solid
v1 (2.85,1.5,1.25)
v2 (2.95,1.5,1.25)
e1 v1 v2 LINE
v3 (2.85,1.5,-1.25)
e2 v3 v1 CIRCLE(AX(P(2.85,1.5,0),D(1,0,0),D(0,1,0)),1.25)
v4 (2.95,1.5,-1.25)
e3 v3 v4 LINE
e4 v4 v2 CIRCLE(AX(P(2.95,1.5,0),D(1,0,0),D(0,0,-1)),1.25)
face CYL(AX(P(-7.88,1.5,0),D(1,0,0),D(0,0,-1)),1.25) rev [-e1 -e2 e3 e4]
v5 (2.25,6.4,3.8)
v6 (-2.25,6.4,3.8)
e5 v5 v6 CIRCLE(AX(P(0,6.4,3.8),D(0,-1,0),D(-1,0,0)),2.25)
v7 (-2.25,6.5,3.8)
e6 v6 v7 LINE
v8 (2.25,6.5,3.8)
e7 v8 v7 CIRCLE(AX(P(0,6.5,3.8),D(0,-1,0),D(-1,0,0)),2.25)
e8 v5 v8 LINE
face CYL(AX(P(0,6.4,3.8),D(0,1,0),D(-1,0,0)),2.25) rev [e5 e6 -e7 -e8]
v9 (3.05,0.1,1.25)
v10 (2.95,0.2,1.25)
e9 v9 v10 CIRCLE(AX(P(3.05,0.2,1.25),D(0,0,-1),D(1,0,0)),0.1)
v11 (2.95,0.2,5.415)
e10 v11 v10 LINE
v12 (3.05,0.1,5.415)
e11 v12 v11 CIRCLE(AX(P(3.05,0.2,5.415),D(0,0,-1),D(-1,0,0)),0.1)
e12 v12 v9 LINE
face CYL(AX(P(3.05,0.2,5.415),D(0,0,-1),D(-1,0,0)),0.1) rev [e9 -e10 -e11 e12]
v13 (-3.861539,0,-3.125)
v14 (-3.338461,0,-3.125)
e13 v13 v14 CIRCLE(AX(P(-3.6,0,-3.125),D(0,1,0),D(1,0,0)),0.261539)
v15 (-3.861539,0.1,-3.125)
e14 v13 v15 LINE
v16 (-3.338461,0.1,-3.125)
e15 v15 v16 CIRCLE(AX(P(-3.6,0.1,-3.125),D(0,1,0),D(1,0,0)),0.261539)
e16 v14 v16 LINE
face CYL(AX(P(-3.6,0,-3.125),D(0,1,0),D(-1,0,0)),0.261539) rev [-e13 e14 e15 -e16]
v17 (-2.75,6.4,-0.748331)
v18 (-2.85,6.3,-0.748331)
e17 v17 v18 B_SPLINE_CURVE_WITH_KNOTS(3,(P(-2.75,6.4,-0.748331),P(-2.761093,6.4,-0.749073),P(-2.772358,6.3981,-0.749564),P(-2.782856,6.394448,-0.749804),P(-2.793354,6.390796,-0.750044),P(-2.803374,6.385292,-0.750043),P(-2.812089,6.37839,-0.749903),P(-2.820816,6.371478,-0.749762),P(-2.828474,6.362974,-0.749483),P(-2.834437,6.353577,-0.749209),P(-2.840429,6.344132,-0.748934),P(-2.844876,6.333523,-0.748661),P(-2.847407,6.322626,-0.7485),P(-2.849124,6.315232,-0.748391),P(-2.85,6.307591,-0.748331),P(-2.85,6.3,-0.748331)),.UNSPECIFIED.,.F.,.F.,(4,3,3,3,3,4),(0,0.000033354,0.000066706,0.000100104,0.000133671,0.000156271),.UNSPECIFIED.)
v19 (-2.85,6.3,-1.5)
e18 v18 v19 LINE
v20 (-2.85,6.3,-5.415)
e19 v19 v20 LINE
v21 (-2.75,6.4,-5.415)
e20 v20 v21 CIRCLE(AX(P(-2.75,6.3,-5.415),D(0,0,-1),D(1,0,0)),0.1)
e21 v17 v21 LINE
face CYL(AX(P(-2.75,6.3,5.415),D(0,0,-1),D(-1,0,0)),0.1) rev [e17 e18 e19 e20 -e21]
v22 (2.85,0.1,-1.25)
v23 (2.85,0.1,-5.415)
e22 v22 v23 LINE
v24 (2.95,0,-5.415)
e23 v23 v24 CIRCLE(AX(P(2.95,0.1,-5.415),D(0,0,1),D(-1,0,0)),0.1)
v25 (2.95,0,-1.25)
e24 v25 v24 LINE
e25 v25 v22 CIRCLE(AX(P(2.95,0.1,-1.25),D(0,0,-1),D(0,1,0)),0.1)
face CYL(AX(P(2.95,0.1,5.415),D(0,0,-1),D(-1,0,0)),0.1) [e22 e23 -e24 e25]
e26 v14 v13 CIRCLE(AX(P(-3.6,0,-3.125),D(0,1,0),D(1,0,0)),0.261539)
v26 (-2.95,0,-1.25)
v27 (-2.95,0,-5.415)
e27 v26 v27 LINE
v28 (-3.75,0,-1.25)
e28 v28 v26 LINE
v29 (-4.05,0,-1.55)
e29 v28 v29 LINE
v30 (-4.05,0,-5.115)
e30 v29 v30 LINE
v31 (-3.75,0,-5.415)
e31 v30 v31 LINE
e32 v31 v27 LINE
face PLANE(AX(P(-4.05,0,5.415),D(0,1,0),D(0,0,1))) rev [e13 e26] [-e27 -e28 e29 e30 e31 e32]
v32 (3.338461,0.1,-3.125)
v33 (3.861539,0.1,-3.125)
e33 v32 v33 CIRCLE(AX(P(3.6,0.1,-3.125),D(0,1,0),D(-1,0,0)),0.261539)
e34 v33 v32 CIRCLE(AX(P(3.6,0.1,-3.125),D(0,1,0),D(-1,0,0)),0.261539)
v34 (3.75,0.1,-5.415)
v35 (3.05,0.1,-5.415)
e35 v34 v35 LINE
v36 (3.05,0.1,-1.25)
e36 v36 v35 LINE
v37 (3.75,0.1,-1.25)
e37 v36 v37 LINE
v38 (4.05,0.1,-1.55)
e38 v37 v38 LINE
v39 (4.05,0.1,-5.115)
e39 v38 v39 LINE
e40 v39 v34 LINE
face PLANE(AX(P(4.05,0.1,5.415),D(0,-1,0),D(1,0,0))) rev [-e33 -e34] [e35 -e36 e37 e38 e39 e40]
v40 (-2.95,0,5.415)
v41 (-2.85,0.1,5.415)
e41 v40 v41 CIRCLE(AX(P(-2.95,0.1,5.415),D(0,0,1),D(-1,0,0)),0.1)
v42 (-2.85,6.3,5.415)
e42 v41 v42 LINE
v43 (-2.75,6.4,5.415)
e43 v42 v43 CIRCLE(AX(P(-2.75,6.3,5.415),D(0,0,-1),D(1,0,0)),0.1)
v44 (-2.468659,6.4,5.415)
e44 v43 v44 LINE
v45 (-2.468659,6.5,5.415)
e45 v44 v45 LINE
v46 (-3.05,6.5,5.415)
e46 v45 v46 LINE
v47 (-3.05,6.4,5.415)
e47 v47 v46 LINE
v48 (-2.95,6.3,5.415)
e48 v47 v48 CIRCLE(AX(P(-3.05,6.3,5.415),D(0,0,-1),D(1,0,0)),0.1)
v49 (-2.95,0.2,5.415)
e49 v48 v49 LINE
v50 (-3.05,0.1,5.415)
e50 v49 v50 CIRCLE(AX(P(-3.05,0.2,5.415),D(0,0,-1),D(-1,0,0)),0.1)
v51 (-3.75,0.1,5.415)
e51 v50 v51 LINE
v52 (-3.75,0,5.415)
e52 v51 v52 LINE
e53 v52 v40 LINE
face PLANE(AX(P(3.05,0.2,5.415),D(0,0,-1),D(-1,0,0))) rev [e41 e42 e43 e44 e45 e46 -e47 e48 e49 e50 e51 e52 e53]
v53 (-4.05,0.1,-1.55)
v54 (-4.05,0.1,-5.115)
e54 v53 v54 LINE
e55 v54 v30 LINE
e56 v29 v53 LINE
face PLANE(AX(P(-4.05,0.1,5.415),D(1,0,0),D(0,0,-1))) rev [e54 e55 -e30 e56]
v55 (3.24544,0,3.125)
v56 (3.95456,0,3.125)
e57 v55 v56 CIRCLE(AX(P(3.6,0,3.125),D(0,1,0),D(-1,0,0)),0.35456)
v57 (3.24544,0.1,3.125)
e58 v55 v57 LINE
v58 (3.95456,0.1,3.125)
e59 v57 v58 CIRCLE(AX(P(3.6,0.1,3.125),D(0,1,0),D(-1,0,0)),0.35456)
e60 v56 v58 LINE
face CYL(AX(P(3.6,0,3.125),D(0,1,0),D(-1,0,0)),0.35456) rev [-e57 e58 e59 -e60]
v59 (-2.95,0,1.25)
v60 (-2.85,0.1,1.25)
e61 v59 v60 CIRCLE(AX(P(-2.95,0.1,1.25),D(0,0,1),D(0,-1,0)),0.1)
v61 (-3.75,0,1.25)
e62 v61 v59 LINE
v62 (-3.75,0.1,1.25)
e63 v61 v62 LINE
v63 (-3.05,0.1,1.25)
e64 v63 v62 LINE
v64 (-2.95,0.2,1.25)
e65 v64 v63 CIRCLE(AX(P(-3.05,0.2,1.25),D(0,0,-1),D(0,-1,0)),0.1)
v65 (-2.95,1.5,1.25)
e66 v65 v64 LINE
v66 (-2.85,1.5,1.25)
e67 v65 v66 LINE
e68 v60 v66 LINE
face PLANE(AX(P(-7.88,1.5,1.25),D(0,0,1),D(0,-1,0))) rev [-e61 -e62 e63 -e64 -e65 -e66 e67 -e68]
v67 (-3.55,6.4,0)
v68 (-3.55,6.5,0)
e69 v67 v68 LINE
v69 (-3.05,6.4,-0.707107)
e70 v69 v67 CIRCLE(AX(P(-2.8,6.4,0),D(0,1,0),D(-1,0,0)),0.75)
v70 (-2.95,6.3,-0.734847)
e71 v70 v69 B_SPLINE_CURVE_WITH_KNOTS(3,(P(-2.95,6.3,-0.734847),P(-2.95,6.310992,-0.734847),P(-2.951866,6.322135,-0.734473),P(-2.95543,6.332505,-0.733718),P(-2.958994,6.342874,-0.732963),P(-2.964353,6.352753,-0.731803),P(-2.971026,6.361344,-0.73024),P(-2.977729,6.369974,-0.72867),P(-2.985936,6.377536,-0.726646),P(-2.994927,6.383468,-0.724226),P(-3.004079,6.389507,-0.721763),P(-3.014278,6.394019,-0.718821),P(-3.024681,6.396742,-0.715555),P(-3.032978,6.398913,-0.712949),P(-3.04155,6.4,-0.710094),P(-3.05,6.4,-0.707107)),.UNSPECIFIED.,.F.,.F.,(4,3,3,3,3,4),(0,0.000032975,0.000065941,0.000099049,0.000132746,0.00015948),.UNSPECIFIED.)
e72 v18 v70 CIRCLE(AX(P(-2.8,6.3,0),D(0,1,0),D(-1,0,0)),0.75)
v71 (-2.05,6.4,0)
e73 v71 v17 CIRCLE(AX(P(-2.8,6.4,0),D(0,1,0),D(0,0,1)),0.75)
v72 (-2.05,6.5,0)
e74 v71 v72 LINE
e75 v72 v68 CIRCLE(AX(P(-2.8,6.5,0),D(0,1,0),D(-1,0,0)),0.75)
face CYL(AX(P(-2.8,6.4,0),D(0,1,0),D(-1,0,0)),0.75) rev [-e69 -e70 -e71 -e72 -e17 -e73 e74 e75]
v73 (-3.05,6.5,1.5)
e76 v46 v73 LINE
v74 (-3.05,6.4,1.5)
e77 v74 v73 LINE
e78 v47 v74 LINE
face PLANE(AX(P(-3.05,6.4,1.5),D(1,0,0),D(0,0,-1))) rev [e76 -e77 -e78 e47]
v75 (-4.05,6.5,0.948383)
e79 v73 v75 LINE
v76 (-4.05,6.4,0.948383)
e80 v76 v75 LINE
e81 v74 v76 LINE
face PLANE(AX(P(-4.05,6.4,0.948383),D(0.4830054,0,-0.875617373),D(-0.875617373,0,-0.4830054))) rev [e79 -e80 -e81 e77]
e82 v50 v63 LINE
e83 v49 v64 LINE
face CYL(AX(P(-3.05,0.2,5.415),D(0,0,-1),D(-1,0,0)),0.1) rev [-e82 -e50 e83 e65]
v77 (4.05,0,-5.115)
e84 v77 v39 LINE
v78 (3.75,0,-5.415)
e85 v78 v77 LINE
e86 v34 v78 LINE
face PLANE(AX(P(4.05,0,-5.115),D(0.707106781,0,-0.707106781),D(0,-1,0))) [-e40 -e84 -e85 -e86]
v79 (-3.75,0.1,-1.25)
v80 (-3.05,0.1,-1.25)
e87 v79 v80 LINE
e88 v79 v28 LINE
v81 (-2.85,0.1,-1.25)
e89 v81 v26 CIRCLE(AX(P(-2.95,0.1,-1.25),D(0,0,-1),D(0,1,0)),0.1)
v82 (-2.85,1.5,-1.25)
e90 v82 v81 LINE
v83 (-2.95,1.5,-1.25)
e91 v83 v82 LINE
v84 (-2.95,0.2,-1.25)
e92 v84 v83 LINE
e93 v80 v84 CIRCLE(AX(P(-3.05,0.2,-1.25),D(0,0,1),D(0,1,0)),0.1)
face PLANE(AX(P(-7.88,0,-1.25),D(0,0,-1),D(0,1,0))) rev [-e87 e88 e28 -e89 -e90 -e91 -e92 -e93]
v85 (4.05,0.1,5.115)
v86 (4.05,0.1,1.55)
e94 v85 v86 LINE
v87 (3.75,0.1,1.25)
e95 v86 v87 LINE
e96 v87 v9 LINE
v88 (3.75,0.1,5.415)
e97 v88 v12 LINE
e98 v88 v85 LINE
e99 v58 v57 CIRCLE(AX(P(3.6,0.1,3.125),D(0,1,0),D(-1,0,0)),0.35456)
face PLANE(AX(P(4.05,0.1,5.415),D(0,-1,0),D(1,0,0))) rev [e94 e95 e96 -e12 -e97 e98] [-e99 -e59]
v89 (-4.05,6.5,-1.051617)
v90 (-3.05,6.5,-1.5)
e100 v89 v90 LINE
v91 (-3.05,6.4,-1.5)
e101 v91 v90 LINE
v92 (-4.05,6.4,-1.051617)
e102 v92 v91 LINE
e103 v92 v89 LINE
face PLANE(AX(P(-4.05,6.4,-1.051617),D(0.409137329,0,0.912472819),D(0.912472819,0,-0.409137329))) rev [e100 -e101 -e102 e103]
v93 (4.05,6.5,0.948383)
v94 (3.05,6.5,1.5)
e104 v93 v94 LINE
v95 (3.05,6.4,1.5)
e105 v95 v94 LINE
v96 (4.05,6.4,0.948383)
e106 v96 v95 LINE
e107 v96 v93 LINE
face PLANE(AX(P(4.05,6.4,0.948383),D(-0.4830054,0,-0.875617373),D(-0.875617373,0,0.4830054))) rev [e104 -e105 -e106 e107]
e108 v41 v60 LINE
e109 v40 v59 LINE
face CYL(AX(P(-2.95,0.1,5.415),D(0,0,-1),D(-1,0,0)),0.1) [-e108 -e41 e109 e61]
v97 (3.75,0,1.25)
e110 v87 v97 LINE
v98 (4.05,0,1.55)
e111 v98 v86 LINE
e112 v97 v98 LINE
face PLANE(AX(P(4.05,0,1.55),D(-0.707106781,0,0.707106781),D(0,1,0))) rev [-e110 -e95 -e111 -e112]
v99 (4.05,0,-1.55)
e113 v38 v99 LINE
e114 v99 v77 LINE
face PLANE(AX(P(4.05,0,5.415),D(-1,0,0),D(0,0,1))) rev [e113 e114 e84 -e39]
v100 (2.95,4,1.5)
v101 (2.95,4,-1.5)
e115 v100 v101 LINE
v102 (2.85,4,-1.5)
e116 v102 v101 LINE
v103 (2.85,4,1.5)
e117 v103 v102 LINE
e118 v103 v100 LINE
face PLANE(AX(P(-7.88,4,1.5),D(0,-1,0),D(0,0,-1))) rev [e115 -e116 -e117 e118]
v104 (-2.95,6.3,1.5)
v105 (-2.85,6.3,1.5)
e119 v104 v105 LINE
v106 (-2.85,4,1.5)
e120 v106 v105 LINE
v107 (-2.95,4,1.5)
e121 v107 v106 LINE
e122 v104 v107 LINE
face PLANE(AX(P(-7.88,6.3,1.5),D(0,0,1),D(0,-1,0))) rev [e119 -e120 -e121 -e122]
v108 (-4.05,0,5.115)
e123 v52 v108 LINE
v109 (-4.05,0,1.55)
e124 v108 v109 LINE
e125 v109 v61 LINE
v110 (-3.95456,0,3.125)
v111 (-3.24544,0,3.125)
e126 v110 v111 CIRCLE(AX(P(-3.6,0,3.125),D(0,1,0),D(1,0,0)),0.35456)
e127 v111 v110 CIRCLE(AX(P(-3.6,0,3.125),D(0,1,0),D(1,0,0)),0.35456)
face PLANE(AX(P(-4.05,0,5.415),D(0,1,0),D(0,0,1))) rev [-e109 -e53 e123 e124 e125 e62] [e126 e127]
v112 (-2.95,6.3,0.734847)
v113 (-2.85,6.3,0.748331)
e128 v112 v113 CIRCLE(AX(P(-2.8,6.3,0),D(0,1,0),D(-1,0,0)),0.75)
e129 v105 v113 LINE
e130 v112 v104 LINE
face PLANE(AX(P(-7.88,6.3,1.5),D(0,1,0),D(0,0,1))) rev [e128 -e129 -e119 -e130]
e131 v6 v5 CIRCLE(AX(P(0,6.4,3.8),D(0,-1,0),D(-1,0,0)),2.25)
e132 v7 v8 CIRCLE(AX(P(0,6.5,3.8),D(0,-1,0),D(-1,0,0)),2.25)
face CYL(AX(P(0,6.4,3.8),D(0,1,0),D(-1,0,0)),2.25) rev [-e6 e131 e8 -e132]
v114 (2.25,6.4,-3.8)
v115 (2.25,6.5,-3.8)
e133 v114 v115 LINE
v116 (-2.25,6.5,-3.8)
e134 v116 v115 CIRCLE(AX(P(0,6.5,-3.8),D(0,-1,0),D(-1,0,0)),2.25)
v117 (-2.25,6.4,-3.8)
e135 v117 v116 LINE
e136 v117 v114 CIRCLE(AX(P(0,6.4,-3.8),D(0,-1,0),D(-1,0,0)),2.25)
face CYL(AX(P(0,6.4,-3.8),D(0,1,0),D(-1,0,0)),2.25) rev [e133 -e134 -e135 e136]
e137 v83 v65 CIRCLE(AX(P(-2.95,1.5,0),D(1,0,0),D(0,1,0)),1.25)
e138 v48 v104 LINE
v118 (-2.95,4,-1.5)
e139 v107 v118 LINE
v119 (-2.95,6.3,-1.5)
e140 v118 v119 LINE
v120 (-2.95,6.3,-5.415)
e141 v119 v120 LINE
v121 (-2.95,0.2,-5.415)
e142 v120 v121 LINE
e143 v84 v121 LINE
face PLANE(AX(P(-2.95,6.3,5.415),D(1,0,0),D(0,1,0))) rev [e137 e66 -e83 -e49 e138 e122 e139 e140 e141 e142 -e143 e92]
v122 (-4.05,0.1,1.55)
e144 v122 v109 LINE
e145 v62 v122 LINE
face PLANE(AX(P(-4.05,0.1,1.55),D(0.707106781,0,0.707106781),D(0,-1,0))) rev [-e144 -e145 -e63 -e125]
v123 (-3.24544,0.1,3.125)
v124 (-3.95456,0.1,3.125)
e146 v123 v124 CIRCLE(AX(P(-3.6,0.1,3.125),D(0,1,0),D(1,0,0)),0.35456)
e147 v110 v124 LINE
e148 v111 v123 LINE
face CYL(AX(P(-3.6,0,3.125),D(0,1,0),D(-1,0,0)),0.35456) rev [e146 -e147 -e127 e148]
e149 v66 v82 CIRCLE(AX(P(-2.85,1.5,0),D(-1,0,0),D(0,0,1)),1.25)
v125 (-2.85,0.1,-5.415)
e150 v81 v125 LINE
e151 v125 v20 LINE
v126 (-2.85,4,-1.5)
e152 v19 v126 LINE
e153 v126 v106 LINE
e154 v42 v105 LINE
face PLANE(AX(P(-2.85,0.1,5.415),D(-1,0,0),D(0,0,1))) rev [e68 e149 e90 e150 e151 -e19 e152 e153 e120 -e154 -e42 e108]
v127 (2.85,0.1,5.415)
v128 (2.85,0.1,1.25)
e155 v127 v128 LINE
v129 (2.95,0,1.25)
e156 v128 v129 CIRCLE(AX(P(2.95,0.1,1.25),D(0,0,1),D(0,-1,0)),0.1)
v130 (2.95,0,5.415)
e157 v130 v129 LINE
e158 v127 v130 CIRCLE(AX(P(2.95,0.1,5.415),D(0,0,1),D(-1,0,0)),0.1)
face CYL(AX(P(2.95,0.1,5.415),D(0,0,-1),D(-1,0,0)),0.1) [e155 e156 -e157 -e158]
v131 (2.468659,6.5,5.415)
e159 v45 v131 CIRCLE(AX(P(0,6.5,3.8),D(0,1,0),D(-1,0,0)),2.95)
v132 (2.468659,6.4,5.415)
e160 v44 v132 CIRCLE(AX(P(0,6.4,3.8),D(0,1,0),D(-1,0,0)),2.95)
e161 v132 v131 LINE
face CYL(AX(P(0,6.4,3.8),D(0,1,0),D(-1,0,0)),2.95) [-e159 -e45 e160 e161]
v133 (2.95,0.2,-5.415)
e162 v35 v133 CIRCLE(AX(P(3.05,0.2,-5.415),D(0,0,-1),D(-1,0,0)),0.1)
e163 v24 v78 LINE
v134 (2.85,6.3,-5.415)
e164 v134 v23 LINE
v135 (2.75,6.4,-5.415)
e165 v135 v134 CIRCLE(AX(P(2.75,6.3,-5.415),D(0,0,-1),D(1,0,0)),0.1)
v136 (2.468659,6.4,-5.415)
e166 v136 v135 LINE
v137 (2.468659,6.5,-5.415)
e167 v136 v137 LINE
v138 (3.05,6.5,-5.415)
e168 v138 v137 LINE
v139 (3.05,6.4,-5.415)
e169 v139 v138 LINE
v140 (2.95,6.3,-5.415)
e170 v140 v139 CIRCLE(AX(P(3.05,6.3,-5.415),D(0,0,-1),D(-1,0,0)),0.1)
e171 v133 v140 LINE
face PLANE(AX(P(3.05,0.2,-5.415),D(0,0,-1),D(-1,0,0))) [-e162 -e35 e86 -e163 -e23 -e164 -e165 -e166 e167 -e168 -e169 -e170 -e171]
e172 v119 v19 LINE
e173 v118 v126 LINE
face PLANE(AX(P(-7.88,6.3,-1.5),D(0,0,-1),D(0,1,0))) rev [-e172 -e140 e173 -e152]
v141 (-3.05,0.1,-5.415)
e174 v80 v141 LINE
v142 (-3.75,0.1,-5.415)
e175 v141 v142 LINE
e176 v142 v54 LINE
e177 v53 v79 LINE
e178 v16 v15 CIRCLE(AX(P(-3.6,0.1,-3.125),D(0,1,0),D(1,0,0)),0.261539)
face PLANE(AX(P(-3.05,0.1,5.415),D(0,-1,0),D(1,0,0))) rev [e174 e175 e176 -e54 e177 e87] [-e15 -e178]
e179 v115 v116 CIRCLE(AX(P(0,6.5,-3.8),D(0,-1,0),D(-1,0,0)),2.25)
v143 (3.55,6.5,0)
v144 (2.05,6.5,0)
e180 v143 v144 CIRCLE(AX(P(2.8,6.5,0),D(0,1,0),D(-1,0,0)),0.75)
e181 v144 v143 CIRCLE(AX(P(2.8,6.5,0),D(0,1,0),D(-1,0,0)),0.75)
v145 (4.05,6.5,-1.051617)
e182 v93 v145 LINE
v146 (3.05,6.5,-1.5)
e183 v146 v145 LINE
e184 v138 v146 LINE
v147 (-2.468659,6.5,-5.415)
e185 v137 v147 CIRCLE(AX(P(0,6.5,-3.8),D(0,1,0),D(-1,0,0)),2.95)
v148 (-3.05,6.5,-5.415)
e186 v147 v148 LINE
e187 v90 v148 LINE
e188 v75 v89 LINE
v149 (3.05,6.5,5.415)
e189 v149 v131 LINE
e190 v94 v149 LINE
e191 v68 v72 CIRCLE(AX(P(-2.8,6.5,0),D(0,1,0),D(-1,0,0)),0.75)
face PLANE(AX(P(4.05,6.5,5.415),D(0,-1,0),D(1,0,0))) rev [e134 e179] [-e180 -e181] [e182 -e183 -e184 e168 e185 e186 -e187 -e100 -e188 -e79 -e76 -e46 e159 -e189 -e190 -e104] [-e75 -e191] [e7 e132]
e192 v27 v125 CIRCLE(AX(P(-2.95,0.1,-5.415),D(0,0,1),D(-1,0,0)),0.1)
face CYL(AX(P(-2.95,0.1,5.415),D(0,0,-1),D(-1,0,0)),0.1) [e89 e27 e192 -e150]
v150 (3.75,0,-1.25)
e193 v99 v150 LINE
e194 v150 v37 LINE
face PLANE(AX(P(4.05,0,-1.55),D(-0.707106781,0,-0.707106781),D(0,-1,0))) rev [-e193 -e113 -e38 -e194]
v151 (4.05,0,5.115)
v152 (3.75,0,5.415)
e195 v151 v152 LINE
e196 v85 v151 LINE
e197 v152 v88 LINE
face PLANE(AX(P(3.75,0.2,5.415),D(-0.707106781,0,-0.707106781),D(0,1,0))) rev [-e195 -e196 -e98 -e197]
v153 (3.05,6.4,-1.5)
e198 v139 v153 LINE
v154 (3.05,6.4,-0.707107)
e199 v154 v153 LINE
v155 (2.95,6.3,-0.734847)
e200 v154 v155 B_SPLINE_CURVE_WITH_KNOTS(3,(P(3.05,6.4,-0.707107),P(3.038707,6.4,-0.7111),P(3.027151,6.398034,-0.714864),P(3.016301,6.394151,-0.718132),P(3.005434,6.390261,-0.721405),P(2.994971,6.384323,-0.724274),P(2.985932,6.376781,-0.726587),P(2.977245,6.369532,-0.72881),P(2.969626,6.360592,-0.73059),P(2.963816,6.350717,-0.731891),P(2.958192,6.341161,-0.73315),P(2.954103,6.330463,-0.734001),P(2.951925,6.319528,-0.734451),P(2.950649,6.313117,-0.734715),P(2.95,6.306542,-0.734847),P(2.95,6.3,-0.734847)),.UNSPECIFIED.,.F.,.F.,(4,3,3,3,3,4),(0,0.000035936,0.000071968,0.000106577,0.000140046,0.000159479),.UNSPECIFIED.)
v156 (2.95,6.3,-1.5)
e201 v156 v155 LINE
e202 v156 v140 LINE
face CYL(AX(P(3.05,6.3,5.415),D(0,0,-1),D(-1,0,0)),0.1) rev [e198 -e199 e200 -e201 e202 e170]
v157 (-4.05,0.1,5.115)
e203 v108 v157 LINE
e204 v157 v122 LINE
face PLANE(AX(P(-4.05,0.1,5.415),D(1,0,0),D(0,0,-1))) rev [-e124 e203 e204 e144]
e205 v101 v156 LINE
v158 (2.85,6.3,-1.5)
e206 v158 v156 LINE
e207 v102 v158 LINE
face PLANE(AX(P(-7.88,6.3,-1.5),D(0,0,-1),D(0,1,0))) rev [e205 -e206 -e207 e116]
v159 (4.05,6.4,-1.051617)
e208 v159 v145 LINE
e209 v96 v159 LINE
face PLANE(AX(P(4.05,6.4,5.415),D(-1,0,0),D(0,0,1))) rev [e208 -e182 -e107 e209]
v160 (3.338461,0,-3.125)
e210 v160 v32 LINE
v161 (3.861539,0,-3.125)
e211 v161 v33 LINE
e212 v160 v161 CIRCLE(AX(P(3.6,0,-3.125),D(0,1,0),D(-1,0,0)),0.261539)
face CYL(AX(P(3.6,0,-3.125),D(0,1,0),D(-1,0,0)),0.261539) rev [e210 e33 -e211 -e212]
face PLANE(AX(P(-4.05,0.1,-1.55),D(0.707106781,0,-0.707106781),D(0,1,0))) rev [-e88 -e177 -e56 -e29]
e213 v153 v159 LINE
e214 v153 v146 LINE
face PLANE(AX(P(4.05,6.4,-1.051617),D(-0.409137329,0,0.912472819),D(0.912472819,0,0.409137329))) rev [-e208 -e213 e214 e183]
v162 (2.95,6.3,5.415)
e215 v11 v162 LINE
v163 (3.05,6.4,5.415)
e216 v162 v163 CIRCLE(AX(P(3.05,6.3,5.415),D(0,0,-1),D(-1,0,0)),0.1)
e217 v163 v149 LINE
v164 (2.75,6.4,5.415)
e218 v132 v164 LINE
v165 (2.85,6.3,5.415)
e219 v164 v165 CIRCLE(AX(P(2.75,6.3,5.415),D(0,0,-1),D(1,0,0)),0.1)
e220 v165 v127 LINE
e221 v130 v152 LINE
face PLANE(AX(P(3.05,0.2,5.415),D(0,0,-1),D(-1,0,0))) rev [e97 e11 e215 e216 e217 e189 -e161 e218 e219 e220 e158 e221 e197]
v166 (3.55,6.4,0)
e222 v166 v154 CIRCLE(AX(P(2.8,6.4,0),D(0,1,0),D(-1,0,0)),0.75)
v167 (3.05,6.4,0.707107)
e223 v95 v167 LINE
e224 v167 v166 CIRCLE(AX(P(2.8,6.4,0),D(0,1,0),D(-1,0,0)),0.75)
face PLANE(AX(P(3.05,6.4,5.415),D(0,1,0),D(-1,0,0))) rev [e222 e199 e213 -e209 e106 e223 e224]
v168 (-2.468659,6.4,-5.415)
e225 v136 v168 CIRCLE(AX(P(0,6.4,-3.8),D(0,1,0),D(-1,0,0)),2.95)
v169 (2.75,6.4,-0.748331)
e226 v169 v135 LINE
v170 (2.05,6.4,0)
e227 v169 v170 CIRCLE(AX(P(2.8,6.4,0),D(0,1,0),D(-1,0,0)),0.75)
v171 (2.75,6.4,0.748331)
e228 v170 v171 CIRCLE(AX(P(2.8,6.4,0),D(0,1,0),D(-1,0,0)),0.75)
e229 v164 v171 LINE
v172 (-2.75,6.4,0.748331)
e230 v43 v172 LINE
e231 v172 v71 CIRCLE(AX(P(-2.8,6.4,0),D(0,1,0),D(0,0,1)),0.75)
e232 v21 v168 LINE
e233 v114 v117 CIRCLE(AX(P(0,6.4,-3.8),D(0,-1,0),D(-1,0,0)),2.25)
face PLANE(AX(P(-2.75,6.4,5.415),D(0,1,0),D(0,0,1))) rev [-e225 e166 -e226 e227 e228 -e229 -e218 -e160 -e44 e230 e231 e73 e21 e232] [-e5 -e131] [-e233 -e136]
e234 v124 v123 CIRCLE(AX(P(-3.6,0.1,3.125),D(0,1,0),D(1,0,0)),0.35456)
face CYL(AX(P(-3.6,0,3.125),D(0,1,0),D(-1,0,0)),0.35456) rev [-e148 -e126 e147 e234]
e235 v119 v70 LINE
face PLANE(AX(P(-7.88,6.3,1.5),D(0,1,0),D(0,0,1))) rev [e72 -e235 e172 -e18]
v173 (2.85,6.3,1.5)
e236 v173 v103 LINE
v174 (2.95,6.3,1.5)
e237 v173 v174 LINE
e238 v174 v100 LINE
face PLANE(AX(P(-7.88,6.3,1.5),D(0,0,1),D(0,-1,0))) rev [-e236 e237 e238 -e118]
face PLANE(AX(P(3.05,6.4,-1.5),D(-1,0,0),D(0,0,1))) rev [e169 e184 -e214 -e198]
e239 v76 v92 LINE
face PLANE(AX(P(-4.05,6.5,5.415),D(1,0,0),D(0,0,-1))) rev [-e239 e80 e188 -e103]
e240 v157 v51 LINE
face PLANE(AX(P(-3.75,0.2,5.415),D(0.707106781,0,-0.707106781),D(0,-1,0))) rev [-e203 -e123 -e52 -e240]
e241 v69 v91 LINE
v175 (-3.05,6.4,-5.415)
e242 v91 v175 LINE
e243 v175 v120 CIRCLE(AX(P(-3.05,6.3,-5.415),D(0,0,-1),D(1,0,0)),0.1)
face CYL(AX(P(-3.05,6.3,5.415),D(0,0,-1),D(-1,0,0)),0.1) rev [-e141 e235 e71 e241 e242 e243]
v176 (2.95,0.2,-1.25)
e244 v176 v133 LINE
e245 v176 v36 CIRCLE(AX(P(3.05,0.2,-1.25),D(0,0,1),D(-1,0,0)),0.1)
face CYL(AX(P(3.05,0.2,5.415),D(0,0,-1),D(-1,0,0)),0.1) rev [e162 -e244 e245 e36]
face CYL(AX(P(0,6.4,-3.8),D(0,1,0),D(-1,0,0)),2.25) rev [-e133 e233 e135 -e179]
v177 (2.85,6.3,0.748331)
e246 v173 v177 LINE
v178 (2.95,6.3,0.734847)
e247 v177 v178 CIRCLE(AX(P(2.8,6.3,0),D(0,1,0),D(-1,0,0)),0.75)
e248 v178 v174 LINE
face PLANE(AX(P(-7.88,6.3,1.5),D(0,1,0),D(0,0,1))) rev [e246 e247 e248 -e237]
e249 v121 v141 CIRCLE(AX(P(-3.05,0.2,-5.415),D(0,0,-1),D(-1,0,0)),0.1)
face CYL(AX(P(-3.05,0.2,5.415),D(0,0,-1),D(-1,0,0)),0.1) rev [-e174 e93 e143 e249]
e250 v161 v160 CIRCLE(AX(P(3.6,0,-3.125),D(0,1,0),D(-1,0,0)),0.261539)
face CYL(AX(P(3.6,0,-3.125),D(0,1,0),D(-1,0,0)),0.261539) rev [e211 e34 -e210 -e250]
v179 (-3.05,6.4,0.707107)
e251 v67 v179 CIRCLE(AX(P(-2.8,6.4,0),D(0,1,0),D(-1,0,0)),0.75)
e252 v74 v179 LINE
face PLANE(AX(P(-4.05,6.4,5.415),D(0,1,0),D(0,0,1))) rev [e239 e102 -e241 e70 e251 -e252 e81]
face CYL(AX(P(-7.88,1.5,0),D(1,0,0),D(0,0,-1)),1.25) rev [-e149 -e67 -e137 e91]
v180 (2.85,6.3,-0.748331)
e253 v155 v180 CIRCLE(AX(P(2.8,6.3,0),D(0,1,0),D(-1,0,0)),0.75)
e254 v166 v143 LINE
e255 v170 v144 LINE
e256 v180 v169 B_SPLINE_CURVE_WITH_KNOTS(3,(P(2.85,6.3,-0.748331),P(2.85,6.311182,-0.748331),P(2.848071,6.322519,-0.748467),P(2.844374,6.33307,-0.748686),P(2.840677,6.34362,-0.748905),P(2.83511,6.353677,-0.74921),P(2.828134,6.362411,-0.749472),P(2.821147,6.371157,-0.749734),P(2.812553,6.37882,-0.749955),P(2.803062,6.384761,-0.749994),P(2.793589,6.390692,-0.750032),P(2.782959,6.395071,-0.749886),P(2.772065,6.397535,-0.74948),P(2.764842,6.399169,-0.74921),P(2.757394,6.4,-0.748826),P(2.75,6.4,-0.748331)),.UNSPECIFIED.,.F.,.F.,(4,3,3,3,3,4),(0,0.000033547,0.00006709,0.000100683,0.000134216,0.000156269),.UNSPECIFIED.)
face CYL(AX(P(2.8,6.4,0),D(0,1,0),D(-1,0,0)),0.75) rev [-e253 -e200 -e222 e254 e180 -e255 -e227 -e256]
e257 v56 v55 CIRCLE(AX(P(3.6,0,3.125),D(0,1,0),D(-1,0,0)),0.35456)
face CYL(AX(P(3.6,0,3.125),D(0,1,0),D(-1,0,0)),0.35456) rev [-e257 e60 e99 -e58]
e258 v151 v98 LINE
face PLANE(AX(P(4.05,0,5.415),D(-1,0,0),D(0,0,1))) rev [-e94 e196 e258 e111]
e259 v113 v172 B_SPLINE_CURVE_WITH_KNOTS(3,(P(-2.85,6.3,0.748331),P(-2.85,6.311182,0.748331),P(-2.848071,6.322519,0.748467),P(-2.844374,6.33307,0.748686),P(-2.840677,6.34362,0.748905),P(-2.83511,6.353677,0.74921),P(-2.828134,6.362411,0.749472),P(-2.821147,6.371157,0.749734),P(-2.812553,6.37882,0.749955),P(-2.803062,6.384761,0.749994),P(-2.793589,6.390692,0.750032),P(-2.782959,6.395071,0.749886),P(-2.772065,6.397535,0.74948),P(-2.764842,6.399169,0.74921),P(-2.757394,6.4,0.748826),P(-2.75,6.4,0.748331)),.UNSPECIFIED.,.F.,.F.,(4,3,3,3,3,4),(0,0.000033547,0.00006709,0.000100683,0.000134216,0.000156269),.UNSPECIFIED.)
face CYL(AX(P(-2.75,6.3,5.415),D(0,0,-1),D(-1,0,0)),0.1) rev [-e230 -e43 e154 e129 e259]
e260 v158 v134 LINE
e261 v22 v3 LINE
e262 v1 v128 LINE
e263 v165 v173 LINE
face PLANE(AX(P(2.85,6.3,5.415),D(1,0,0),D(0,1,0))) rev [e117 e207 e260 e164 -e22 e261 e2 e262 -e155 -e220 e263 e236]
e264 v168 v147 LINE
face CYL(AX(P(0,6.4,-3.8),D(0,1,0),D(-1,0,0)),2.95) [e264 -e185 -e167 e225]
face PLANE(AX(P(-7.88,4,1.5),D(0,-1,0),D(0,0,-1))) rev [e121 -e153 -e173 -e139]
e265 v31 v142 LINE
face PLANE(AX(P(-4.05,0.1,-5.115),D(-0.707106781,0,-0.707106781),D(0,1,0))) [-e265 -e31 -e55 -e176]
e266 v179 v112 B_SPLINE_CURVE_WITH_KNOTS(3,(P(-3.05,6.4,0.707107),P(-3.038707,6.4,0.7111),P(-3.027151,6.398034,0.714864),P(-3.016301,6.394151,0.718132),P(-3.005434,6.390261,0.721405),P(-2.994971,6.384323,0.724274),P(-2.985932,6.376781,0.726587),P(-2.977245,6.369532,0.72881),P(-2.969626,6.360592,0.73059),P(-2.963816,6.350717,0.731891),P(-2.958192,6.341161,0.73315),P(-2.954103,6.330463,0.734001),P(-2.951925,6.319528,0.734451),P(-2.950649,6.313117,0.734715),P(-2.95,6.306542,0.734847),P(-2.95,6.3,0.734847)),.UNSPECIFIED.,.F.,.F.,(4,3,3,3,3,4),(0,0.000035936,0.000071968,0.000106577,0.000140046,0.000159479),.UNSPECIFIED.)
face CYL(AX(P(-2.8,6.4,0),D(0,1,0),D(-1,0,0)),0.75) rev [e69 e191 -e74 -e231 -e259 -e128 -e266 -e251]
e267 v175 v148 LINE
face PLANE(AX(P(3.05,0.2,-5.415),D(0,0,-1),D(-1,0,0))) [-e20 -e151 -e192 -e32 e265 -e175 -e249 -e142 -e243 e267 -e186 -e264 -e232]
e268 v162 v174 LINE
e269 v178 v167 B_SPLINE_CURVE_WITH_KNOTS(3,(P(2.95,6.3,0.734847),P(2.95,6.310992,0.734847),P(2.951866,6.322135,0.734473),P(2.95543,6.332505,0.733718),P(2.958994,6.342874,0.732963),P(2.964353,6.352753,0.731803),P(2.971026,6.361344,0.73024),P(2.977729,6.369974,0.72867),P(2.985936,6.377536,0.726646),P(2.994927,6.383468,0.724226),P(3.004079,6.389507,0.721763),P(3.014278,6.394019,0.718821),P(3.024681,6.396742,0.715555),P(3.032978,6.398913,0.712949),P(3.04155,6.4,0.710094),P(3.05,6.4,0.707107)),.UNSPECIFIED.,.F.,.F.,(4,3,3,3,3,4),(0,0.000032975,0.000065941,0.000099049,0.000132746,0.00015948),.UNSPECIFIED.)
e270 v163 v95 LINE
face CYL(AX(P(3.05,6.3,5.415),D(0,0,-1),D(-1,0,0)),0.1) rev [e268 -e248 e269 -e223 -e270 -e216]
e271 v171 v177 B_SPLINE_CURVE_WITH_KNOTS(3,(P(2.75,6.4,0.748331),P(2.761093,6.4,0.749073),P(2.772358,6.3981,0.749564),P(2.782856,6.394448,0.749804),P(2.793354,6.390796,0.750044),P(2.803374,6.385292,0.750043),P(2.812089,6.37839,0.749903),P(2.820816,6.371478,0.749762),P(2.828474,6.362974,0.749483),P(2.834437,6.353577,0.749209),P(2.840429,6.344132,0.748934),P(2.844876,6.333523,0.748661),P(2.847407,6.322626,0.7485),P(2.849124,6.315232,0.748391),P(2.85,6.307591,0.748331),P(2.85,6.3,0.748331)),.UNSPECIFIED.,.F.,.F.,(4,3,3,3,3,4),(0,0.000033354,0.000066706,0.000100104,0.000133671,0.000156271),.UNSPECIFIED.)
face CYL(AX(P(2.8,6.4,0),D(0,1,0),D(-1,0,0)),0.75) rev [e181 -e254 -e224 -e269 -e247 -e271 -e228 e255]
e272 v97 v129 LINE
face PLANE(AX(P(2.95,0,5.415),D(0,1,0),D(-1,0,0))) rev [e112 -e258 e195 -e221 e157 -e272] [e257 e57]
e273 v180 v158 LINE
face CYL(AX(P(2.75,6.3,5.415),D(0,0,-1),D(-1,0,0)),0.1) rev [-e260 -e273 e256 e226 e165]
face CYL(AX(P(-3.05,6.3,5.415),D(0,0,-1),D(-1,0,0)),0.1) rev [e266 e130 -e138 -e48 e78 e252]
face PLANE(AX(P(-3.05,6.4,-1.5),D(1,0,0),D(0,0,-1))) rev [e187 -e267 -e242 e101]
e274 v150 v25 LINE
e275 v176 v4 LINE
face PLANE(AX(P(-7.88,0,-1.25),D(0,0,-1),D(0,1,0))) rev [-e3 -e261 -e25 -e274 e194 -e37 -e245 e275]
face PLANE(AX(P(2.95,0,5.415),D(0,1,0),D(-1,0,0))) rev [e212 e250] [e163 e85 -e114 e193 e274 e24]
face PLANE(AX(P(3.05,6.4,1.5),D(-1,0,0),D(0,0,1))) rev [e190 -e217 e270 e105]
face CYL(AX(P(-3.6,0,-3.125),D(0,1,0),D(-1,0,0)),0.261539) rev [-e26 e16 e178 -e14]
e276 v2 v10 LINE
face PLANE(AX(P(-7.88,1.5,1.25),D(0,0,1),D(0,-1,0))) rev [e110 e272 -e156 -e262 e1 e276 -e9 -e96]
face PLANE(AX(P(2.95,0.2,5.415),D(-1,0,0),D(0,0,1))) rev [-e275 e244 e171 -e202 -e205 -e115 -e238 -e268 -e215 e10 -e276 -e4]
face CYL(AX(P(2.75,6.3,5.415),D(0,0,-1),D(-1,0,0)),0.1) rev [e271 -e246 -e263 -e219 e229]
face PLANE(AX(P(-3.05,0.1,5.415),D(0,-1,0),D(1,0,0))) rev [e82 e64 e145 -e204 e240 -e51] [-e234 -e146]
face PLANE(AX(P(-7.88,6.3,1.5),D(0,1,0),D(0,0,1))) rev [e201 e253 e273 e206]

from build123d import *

# Parameters (mm, degrees)
BRACKET_CHANNEL_BODY_DEPTH     = 5.415
SIDE_ARCH_CUT_A_DEPTH          = 10.83
SIDE_WINDOW_CUT_SKETCH_W       = 2.5
SIDE_WINDOW_CUT_SKETCH_H       = 0.2
SIDE_WINDOW_CUT_DEPTH          = 10.83
SIDE_ARCH_CUT_B_SKETCH_W       = 3
SIDE_ARCH_CUT_B_SKETCH_H       = 2.3
SIDE_ARCH_CUT_B_DEPTH          = 10.83
TOP_PLATE_LUGS_DEPTH           = 0.1
LUG_TRIM_CUT_SKETCH_R          = 2.25
LUG_TRIM_CUT_DEPTH             = 0.1
LARGE_HOLES_2XD2_8_SKETCH_R    = 0.75
LARGE_HOLES_2XD2_8_DEPTH       = 0.1
HOLE_CUT_A_SKETCH_R            = 0.75
HOLE_CUT_A_DEPTH               = 0.1
PROFILE_TRIM_CUT_DEPTH         = 0.1
SMALL_HOLES_2XD0_45_SKETCH_R   = 0.261538798
SMALL_HOLES_2XD0_45_SKETCH_R_2 = 0.354559983
SMALL_HOLES_2XD0_45_DEPTH      = 0.1
HOLE_CUT_B_SKETCH_R            = 0.75
HOLE_CUT_B_DEPTH               = 0.1
EDGE_CHAMFER_0_3_SIZE          = 0.3
ARCH_EDGE_CHAMFER_0_3_SIZE     = 0.3


with BuildPart() as part:
    # Channel Profile Sketch → Bracket Channel Body (new, symmetric)
    with BuildSketch(Plane.XY):
        with BuildLine():
            ThreePointArc((-2.95, 0), (-2.879289322, 0.029289322), (-2.85, 0.1))
            Line((-2.85, 0.1), (-2.85, 6.3))
            ThreePointArc((-2.85, 6.3), (-2.820710678, 6.370710678), (-2.75, 6.4))
            Line((-2.75, 6.4), (2.75, 6.4))
            ThreePointArc((2.75, 6.4), (2.820710678, 6.370710678), (2.85, 6.3))
            Line((2.85, 6.3), (2.85, 0.1))
            ThreePointArc((2.85, 0.1), (2.879289322, 0.029289322), (2.95, 0))
            Line((2.95, 0), (4.05, 0))
            Line((4.05, 0), (4.05, 0.1))
            Line((4.05, 0.1), (3.05, 0.1))
            ThreePointArc((3.05, 0.1), (2.979289322, 0.129289322), (2.95, 0.2))
            Line((2.95, 0.2), (2.95, 6.3))
            ThreePointArc((2.95, 6.3), (2.979289322, 6.370710678), (3.05, 6.4))
            Line((3.05, 6.4), (4.05, 6.4))
            Line((4.05, 6.4), (4.05, 6.5))
            Line((4.05, 6.5), (-4.05, 6.5))
            Line((-4.05, 6.5), (-4.05, 6.4))
            Line((-4.05, 6.4), (-3.05, 6.4))
            ThreePointArc((-3.05, 6.4), (-2.979289322, 6.370710678), (-2.95, 6.3))
            Line((-2.95, 6.3), (-2.95, 0.2))
            ThreePointArc((-2.95, 0.2), (-2.979289322, 0.129289322), (-3.05, 0.1))
            Line((-3.05, 0.1), (-4.05, 0.1))
            Line((-4.05, 0.1), (-4.05, 0))
            Line((-4.05, 0), (-2.95, 0))
        make_face()
    extrude(amount=BRACKET_CHANNEL_BODY_DEPTH, both=True)

    # Side Arch Cut A Sketch → Side Arch Cut A (cut)
    with BuildSketch(Plane(origin=(2.95, 0, 0), x_dir=(0, 0, -1), z_dir=(1, 0, 0))):
        with BuildLine():
            Line((-1.25, 1.5), (-1.25, 0))
            Line((-1.25, 0), (1.25, 0))
            Line((1.25, 0), (1.25, 1.5))
            ThreePointArc((1.25, 1.5), (0, 2.75), (-1.25, 1.5))
        make_face()
    extrude(amount=-SIDE_ARCH_CUT_A_DEPTH, mode=Mode.SUBTRACT)

    # Side Window Cut Sketch → Side Window Cut (cut)
    with BuildSketch(Plane.ZY.offset(2.95)):
        with Locations((0, 0.1)):
            Rectangle(SIDE_WINDOW_CUT_SKETCH_W, SIDE_WINDOW_CUT_SKETCH_H)
    extrude(amount=-SIDE_WINDOW_CUT_DEPTH, mode=Mode.SUBTRACT)

    # Side Arch Cut B Sketch → Side Arch Cut B (cut)
    with BuildSketch(Plane(origin=(2.95, 0, 0), x_dir=(0, 0, -1), z_dir=(1, 0, 0))):
        with Locations((0, 5.15)):
            Rectangle(SIDE_ARCH_CUT_B_SKETCH_W, SIDE_ARCH_CUT_B_SKETCH_H)
    extrude(amount=-SIDE_ARCH_CUT_B_DEPTH, mode=Mode.SUBTRACT)

    # Top Plate Lugs Sketch → Top Plate Lugs (add)
    with BuildSketch(Plane(origin=(0, 6.5, 0), x_dir=(1, 0, 0), z_dir=(0, 1, 0))):
        with BuildLine():
            Line((-2.468658543, 5.415), (-1.566612588, 5.415))
            ThreePointArc((-1.566612588, 5.415), (0, 6.05), (1.566612588, 5.415))
            Line((1.566612588, 5.415), (2.468658543, 5.415))
            ThreePointArc((2.468658543, 5.415), (0, 6.75), (-2.468658543, 5.415))
        make_face()
        with BuildLine():
            Line((-2.468658543, -5.415), (-1.566612588, -5.415))
            ThreePointArc((-1.566612588, -5.415), (0, -6.05), (1.566612588, -5.415))
            Line((1.566612588, -5.415), (2.468658543, -5.415))
            ThreePointArc((2.468658543, -5.415), (0, -6.75), (-2.468658543, -5.415))
        make_face()
    extrude(amount=-TOP_PLATE_LUGS_DEPTH)

    # Lug Trim Cut Sketch → Lug Trim Cut (cut)
    with BuildSketch(Plane(origin=(0, 6.5, 0), x_dir=(1, 0, 0), z_dir=(0, 1, 0))):
        with Locations(Location((0, 3.8, 0), (0, 0, 180))):
            Circle(LUG_TRIM_CUT_SKETCH_R)
        with Locations(Location((0, -3.8, 0), (0, 0, 180))):
            Circle(LUG_TRIM_CUT_SKETCH_R)
    extrude(amount=-LUG_TRIM_CUT_DEPTH, mode=Mode.SUBTRACT)

    # Large Holes 2xD2.8 Sketch → Large Holes 2xD2.8 (cut)
    with BuildSketch(Plane(origin=(0, 6.5, 0), x_dir=(1, 0, 0), z_dir=(0, 1, 0))):
        with Locations(Location((2.8, 0, 0), (0, 0, 180))):
            Circle(LARGE_HOLES_2XD2_8_SKETCH_R)
        with Locations(Location((-2.8, 0, 0), (0, 0, 180))):
            Circle(LARGE_HOLES_2XD2_8_SKETCH_R)
    extrude(amount=-LARGE_HOLES_2XD2_8_DEPTH, mode=Mode.SUBTRACT)

    # Hole Cut A Sketch → Hole Cut A (cut)
    with BuildSketch(Plane(origin=(0, 6.4, 0), x_dir=(1, 0, 0), z_dir=(0, 1, 0))):
        with Locations(Location((2.8, 0, 0), (0, 0, 180))):
            Circle(HOLE_CUT_A_SKETCH_R)
    extrude(amount=-HOLE_CUT_A_DEPTH, mode=Mode.SUBTRACT)

    # Profile Trim Cut Sketch → Profile Trim Cut (cut)
    with BuildSketch(Plane(origin=(0, 6.5, 0), x_dir=(1, 0, 0), z_dir=(0, 1, 0))):
        Polygon((-4.05, 1.051616968), (-3.05, 1.5), (-3.05, 5.415), (-4.05, 5.415), align=None)
        Polygon((-4.05, -0.948383032), (-3.05, -1.5), (-3.05, -5.415), (-4.05, -5.415), align=None)
        Polygon((3.05, -1.5), (3.05, -5.415), (4.05, -5.415), (4.05, -0.948383032), align=None)
        Polygon((4.05, 5.415), (4.05, 1.051616968), (3.05, 1.5), (3.05, 5.415), align=None)
    extrude(amount=-PROFILE_TRIM_CUT_DEPTH, mode=Mode.SUBTRACT)

    # Small Holes 2xD0.45 Sketch → Small Holes 2xD0.45 (cut)
    with BuildSketch(Plane(origin=(0, 0.1, 0), x_dir=(1, 0, 0), z_dir=(0, 1, 0))):
        with Locations(Location((3.6, 3.125, 0), (0, 0, 180))):
            Circle(SMALL_HOLES_2XD0_45_SKETCH_R)
        with Locations(Location((3.6, -3.125, 0), (0, 0, 180))):
            Circle(SMALL_HOLES_2XD0_45_SKETCH_R_2)
        with Locations((-3.6, -3.125)):
            Circle(SMALL_HOLES_2XD0_45_SKETCH_R_2)
        with Locations((-3.6, 3.125)):
            Circle(SMALL_HOLES_2XD0_45_SKETCH_R)
    extrude(amount=-SMALL_HOLES_2XD0_45_DEPTH, mode=Mode.SUBTRACT)

    # Hole Cut B Sketch → Hole Cut B (cut)
    with BuildSketch(Plane(origin=(0, 6.4, 0), x_dir=(1, 0, 0), z_dir=(0, 1, 0))):
        with Locations(Location((-2.8, 0, 0), (0, 0, 180))):
            Circle(HOLE_CUT_B_SKETCH_R)
    extrude(amount=-HOLE_CUT_B_DEPTH, mode=Mode.SUBTRACT)

    # Edge Chamfer 0.3
    edge_chamfer_0_3_edges = [part.edges().sort_by_distance(p)[0] for p in [
        (4.05, 0.05, 5.415),
    ]]
    chamfer(edge_chamfer_0_3_edges, length=EDGE_CHAMFER_0_3_SIZE)

    # Arch Edge Chamfer 0.3
    arch_edge_chamfer_0_3_edges = [part.edges().sort_by_distance(p)[0] for p in [
        (4.05, 0.05, 1.25),
        (4.05, 0.05, -1.25),
        (-4.05, 0.05, -5.415),
        (4.05, 0.05, -5.415),
        (-4.05, 0.05, 5.415),
        (-4.05, 0.05, -1.25),
        (-4.05, 0.05, 1.25),
    ]]
    chamfer(arch_edge_chamfer_0_3_edges, length=ARCH_EDGE_CHAMFER_0_3_SIZE)


solid = part.part
